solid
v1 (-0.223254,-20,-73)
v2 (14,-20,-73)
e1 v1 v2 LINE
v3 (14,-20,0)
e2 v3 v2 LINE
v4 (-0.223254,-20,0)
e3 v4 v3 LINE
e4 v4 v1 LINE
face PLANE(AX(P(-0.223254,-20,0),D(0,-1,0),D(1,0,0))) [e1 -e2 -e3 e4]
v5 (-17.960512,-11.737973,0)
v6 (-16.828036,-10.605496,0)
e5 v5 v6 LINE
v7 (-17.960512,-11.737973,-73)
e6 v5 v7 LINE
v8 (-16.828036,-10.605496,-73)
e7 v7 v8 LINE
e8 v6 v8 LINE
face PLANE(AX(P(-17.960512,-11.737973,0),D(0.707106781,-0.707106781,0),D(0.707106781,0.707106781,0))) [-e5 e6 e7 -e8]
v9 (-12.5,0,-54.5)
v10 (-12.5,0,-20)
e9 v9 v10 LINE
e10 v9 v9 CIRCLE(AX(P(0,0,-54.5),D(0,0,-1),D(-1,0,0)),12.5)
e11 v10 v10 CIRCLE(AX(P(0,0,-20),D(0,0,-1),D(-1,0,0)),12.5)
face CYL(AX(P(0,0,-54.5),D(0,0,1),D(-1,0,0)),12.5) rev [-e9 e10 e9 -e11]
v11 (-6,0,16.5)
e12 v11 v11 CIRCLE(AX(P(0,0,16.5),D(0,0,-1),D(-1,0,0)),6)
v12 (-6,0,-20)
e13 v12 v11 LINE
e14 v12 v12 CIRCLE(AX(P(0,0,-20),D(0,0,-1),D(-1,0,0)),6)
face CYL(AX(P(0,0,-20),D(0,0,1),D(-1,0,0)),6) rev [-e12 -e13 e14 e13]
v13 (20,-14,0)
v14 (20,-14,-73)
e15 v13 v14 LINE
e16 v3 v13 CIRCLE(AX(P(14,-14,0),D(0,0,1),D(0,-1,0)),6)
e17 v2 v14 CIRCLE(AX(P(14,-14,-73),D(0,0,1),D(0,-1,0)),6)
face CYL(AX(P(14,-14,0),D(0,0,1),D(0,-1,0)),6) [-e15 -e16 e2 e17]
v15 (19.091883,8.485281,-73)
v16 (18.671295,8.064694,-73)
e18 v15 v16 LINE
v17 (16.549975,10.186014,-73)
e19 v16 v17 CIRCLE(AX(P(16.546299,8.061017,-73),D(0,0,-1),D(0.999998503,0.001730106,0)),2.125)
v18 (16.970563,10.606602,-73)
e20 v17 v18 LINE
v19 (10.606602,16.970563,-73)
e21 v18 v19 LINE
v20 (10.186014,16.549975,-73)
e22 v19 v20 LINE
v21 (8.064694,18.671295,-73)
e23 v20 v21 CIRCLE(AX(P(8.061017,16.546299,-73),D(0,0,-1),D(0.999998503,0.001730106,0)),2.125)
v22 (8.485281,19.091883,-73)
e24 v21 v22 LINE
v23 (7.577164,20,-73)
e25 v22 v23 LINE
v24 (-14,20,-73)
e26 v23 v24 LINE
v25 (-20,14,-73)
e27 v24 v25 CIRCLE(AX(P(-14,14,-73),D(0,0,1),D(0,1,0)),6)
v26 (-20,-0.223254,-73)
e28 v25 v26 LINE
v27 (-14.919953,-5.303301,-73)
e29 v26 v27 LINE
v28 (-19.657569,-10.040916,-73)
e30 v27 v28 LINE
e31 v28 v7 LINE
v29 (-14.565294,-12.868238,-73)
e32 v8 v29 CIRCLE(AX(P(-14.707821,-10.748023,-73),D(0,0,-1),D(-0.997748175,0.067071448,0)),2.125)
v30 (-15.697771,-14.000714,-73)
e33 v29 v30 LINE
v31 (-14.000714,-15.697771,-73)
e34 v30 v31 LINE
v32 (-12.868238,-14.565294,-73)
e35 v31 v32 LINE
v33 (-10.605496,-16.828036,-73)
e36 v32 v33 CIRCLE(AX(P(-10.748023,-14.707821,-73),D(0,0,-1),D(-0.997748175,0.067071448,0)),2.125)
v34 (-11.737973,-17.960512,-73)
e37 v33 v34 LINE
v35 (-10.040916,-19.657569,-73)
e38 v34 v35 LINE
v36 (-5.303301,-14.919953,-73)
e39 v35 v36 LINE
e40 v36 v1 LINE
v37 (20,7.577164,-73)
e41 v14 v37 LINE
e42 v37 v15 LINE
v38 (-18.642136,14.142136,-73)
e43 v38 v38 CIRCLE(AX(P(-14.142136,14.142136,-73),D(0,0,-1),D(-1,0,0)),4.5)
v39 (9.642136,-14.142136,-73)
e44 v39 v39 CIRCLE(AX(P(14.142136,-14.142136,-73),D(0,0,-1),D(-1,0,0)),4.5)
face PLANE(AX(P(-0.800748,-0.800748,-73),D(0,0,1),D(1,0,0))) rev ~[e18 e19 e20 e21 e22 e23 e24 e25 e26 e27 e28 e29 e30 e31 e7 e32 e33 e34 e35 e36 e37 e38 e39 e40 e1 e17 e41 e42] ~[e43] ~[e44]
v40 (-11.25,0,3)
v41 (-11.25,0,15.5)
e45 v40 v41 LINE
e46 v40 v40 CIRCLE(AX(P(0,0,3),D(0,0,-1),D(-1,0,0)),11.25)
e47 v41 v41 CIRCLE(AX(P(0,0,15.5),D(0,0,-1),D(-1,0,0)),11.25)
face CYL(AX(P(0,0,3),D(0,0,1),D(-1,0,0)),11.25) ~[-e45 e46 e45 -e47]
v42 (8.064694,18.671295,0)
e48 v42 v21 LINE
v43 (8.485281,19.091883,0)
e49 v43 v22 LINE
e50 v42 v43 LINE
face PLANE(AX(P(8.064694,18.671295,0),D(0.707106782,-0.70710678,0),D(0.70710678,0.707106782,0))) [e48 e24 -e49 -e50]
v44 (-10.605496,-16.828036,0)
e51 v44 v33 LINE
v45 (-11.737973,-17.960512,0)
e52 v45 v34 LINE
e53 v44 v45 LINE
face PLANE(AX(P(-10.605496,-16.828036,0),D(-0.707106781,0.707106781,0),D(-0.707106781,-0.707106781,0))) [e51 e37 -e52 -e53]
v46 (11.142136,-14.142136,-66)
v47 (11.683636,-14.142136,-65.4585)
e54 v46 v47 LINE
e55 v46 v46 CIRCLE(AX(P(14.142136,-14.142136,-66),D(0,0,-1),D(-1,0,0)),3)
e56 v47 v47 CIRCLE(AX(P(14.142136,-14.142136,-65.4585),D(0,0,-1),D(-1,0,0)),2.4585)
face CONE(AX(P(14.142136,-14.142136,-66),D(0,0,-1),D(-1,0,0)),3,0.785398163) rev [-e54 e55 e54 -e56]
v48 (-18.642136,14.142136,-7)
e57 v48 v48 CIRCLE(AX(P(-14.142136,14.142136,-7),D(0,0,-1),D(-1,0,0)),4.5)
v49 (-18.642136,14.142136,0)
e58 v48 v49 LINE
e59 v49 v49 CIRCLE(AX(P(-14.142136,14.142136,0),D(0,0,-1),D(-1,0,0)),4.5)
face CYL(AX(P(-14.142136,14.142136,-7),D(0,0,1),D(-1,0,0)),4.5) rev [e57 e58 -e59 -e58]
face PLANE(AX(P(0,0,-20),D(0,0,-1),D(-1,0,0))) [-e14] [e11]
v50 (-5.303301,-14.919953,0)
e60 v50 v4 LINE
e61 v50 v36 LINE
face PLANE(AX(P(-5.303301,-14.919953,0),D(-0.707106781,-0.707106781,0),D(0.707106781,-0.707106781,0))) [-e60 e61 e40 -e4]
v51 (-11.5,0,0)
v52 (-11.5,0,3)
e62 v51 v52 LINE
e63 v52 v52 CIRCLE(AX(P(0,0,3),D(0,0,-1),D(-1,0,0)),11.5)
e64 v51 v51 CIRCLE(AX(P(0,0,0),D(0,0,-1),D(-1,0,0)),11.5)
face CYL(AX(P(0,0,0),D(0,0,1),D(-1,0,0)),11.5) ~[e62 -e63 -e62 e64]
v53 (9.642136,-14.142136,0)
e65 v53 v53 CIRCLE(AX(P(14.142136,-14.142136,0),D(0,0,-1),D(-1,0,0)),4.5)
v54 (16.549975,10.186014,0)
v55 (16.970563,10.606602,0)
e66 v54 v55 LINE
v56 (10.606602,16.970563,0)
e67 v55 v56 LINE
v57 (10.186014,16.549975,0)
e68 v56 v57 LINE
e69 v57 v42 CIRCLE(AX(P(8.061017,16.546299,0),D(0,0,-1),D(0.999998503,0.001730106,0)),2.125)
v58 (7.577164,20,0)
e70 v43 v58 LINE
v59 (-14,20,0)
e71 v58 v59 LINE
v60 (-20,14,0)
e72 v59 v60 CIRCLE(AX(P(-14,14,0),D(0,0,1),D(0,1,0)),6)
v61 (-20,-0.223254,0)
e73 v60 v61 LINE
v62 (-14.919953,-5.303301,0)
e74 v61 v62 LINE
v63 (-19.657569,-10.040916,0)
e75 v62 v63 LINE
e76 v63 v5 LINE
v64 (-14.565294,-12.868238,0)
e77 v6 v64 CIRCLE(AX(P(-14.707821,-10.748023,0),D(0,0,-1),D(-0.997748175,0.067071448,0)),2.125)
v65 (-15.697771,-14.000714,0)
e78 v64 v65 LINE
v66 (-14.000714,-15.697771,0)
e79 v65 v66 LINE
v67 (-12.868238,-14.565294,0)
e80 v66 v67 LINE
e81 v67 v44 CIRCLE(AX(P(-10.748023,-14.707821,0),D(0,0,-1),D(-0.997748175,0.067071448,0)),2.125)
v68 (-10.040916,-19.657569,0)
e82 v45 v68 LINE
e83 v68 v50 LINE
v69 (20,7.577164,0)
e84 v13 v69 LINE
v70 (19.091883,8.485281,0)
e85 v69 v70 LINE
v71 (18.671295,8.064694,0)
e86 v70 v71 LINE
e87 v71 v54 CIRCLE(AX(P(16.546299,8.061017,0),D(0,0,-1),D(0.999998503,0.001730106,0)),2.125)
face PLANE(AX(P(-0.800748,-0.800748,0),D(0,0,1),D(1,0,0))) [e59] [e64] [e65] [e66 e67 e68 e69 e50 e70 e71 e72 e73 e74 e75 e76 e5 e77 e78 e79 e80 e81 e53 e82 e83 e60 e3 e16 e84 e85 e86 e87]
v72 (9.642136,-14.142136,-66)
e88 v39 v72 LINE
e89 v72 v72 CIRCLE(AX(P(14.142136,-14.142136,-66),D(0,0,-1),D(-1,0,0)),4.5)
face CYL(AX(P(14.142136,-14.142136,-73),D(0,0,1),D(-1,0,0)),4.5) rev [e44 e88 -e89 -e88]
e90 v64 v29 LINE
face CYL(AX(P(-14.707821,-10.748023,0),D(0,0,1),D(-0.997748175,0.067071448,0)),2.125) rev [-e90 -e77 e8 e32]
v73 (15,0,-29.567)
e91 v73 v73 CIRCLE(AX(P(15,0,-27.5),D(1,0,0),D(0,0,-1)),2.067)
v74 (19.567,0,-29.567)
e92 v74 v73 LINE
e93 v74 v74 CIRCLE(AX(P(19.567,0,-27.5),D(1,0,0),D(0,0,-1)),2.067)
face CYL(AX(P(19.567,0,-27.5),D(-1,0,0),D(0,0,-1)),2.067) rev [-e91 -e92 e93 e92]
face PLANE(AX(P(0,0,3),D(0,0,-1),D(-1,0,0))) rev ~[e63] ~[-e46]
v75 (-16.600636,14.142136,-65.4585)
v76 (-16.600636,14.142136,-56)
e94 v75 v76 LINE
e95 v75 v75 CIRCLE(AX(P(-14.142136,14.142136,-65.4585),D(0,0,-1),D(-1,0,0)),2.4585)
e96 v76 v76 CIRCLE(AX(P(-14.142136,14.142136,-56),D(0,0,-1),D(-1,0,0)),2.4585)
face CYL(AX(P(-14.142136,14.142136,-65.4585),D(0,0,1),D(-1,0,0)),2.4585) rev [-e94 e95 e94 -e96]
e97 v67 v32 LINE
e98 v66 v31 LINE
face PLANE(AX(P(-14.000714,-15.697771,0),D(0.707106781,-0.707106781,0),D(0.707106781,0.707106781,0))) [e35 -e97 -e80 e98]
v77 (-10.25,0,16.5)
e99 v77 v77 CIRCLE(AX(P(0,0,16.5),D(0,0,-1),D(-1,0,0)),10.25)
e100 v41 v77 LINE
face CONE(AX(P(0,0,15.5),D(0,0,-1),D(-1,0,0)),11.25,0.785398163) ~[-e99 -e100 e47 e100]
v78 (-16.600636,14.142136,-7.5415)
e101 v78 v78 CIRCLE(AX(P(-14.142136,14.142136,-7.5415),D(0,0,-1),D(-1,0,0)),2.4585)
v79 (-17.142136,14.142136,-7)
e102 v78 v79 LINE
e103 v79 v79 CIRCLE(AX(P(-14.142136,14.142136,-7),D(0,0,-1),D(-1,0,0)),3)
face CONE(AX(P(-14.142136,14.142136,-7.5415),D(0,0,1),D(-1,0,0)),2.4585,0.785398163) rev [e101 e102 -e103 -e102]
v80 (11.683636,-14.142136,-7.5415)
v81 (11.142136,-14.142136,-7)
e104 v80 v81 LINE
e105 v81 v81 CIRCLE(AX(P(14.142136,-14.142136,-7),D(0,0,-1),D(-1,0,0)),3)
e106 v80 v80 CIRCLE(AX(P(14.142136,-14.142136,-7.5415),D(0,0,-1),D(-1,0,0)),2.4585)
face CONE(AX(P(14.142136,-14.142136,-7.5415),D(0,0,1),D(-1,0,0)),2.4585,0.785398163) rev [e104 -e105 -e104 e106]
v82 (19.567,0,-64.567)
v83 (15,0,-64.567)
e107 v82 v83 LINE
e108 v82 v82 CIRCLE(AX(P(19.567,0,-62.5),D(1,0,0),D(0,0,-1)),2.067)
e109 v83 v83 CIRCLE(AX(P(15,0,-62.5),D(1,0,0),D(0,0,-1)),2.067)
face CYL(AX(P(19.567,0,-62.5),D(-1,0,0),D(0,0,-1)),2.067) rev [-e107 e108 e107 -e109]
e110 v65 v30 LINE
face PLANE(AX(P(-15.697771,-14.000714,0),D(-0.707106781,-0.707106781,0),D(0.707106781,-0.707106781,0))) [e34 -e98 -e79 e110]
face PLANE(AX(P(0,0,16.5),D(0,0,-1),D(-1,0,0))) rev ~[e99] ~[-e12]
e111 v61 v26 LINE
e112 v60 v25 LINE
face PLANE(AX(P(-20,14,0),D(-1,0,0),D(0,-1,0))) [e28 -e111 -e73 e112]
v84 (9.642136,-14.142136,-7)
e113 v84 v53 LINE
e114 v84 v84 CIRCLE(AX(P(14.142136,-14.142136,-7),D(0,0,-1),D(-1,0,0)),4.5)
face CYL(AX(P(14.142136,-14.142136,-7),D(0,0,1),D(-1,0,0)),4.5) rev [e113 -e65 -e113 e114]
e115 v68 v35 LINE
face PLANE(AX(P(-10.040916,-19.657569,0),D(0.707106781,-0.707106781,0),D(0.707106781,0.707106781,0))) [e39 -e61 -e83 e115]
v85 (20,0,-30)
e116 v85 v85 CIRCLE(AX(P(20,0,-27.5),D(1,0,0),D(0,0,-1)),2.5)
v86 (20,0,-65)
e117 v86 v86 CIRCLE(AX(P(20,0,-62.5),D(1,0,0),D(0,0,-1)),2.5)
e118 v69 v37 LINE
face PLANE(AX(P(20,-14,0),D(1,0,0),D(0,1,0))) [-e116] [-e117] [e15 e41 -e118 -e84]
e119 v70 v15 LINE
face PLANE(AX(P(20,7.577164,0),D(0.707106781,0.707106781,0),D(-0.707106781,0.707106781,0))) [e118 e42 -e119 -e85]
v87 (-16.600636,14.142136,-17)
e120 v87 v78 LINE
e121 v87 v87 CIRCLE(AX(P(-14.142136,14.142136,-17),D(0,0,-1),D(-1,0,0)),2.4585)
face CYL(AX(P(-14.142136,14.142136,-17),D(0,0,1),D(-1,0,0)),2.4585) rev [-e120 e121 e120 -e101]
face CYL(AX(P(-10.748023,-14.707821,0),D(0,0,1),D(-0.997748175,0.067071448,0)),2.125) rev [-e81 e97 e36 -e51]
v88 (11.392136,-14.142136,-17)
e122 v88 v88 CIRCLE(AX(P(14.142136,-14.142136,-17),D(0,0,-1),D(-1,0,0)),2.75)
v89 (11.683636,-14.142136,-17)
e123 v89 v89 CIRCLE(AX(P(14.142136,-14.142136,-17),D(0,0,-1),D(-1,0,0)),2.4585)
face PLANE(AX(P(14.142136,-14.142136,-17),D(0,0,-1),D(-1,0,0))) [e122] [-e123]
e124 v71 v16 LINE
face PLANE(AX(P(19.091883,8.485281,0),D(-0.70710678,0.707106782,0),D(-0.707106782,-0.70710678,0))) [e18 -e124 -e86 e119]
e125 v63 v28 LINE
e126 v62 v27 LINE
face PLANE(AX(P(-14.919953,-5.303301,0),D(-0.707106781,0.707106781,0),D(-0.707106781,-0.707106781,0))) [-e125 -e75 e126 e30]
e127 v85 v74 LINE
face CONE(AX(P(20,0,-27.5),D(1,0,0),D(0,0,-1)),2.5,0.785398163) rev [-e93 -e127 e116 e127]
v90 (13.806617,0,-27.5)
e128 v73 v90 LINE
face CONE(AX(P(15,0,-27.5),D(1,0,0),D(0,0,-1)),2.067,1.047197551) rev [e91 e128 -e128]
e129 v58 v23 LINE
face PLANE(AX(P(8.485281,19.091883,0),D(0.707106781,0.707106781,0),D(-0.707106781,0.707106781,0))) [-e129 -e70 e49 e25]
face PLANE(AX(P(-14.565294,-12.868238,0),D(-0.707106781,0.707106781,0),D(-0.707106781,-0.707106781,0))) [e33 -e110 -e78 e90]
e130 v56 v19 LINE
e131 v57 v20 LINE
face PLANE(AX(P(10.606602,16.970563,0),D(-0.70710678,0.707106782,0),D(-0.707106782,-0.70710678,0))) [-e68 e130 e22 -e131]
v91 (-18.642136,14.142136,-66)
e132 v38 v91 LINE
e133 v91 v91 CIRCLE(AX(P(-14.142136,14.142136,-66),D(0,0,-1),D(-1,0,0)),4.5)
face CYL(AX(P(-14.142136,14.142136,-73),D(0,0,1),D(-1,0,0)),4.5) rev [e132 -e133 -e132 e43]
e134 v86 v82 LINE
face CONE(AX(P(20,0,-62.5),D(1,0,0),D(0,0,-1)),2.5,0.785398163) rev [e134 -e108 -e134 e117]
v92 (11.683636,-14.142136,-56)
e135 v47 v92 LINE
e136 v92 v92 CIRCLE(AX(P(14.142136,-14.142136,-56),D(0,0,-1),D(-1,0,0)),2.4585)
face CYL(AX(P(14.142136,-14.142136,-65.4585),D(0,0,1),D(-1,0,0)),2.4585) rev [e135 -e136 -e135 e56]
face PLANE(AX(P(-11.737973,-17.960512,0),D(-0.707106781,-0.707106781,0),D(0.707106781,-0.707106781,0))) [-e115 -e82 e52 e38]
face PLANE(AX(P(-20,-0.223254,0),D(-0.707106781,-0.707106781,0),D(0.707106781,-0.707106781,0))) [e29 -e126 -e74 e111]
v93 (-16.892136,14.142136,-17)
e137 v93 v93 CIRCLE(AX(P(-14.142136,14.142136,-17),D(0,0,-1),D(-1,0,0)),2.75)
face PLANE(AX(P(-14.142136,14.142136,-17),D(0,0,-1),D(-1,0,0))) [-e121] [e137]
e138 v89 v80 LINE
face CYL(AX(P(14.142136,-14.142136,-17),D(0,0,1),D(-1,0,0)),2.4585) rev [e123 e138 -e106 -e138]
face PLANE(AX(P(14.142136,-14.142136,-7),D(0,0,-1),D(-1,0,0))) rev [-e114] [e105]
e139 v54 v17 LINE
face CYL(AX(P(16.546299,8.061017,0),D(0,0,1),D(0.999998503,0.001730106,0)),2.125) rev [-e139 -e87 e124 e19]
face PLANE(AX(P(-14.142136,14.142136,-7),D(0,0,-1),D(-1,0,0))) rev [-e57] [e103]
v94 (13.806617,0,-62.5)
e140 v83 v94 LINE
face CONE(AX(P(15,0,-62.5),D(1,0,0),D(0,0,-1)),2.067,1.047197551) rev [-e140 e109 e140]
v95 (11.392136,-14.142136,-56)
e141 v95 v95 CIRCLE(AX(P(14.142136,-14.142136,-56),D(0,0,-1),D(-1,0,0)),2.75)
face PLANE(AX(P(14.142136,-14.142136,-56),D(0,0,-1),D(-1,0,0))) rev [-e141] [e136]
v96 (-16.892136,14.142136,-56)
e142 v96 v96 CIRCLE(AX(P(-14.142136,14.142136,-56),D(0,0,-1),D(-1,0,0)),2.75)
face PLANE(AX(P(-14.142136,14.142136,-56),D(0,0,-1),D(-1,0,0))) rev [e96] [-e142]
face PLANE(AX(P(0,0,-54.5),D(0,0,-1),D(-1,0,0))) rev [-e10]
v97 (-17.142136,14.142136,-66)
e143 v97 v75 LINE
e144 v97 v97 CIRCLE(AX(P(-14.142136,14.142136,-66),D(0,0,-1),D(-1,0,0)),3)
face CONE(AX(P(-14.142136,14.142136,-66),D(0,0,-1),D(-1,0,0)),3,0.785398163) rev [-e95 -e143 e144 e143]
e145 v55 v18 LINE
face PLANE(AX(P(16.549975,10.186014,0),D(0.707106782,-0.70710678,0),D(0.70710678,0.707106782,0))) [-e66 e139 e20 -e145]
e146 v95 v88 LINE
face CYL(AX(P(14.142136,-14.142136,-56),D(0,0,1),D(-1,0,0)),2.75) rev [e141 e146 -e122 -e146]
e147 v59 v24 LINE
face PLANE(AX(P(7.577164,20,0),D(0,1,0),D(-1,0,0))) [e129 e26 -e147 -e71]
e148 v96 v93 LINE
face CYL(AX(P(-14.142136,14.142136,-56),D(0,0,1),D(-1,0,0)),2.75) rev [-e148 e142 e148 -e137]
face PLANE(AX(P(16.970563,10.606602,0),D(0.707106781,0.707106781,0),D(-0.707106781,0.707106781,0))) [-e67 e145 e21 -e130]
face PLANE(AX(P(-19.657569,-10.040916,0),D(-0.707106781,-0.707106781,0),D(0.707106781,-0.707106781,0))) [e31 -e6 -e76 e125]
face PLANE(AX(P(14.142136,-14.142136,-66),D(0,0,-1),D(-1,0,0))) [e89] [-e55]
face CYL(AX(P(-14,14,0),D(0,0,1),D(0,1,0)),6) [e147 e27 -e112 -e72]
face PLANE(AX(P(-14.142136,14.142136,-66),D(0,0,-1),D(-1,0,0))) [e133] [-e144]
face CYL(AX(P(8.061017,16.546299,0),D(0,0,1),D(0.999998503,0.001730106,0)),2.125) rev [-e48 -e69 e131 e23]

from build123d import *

# Parameters (mm, degrees)
EXTRUDE_1_DEPTH = 73


with BuildPart() as part:
    # 草图1 → 凸台-拉伸1 (new body)
    with BuildSketch(Plane.XY):
        with BuildLine():
            Line((-20, 14), (-20, -0.223253942))
            Line((-20, -0.223253942), (-14.919953083, -5.303300859))
            Line((-14.919953083, -5.303300859), (-19.657568517, -10.040916293))
            Line((-19.657568517, -10.040916293), (-17.960512242, -11.737972568))
            Line((-17.960512242, -11.737972568), (-16.828035921, -10.605496246))
            ThreePointArc((-16.828035921, -10.605496246), (-13.205219139, -9.245421164), (-14.565294221, -12.868237946))
            Line((-14.565294221, -12.868237946), (-15.697770542, -14.000714267))
            Line((-15.697770542, -14.000714267), (-14.000714267, -15.697770542))
            Line((-14.000714267, -15.697770542), (-12.868237946, -14.565294221))
            ThreePointArc((-12.868237946, -14.565294221), (-9.245421164, -13.205219139), (-10.605496246, -16.828035921))
            Line((-10.605496246, -16.828035921), (-11.737972568, -17.960512242))
            Line((-11.737972568, -17.960512242), (-10.040916293, -19.657568517))
            Line((-10.040916293, -19.657568517), (-5.303300859, -14.919953083))
            Line((-5.303300859, -14.919953083), (-0.223253942, -20))
            Line((-0.223253942, -20), (14, -20))
            ThreePointArc((14, -20), (18.242640687, -18.242640687), (20, -14))
            Line((20, -14), (20, 7.577164466))
            Line((20, 7.577164466), (19.091883092, 8.485281374))
            Line((19.091883092, 8.485281374), (18.671295499, 8.064693782))
            ThreePointArc((18.671295499, 8.064693782), (15.04369677, 6.558415396), (16.549975156, 10.186014125))
            Line((16.549975156, 10.186014125), (16.970562748, 10.606601718))
            Line((16.970562748, 10.606601718), (10.606601718, 16.970562748))
            Line((10.606601718, 16.970562748), (10.186014125, 16.549975156))
            ThreePointArc((10.186014125, 16.549975156), (6.558415396, 15.04369677), (8.064693782, 18.671295499))
            Line((8.064693782, 18.671295499), (8.485281374, 19.091883092))
            Line((8.485281374, 19.091883092), (7.577164466, 20))
            Line((7.577164466, 20), (-14, 20))
            ThreePointArc((-14, 20), (-18.242640687, 18.242640687), (-20, 14))
        make_face()
    extrude(amount=-EXTRUDE_1_DEPTH)

    # 草图2 → 切除-旋转1 (revolve, cut)
    with BuildSketch(Plane(origin=(0, 0, 0), x_dir=(0.7071067811865476, -0.7071067811865475, 0), z_dir=(0.7071067811865475, 0.7071067811865476, 0)), mode=Mode.PRIVATE) as cut_revolve_1_sk:
        Polygon((20, 73), (24.5, 73), (24.5, 66), (23, 66), (22.4585, 65.4585), (22.4585, 56), (22.75, 56), (22.75, 17), (22.4585, 17), (22.4585, 7.5415), (23, 7), (24.5, 7), (24.5, 0), (20, 0), align=None)
    revolve(cut_revolve_1_sk.sketch.rotate(Axis((14.142135624, -14.142135624, 0), (0, 0, -1)), 135), axis=Axis((14.142135624, -14.142135624, 0), (0, 0, -1)), mode=Mode.SUBTRACT)

    # 草图3 → 切除-旋转2 (revolve, cut)
    with BuildSketch(Plane(origin=(0, 0, 0), x_dir=(0.7071067811865476, -0.7071067811865475, 0), z_dir=(0.7071067811865475, 0.7071067811865476, 0)), mode=Mode.PRIVATE) as cut_revolve_2_sk:
        Polygon((-20, 73), (-15.5, 73), (-15.5, 66), (-17, 66), (-17.5415, 65.4585), (-17.5415, 56), (-17.25, 56), (-17.25, 17), (-17.5415, 17), (-17.5415, 7.5415), (-17, 7), (-15.5, 7), (-15.5, 0), (-20, 0), align=None)
    revolve(cut_revolve_2_sk.sketch.rotate(Axis((-14.142135624, 14.142135624, 0), (0, 0, -1)), 135), axis=Axis((-14.142135624, 14.142135624, 0), (0, 0, -1)), mode=Mode.SUBTRACT)

    # 草图4 → 旋转1 (revolve)
    with BuildSketch(Plane(origin=(0, 0, 0), x_dir=(1, 0, 0), z_dir=(0, 1, 0)), mode=Mode.PRIVATE) as revolve_1_sk:
        Polygon((0, 0), (11.5, 0), (11.5, -3), (11.25, -3), (11.25, -15.5), (10.25, -16.5), (0, -16.5), align=None)
    revolve(revolve_1_sk.sketch.rotate(Axis((0, 0, 16.5), (0, 0, -1)), 180), axis=Axis((0, 0, 16.5), (0, 0, -1)))

    # 草图5 → 切除-旋转3 (revolve, cut)
    with BuildSketch(Plane(origin=(0, 0, 0), x_dir=(1, 0, 0), z_dir=(0, 1, 0)), mode=Mode.PRIVATE) as cut_revolve_3_sk:
        Polygon((0, 54.5), (12.5, 54.5), (12.5, 20), (6, 20), (6, -16.5), (0, -16.5), align=None)
    revolve(cut_revolve_3_sk.sketch.rotate(Axis((0, 0, 16.5), (0, 0, -1)), 180), axis=Axis((0, 0, 16.5), (0, 0, -1)), mode=Mode.SUBTRACT)

    # 草图6 → 切除-旋转4 (revolve, cut)
    with BuildSketch(Plane(origin=(0, 0, 0), x_dir=(1, 0, 0), z_dir=(0, 1, 0)), mode=Mode.PRIVATE) as cut_revolve_4_sk:
        Polygon((20, 27.5), (20, 25), (19.567, 25.433), (15, 25.433), (13.806616994, 27.5), align=None)
    revolve(cut_revolve_4_sk.sketch.rotate(Axis((13.806616994, 0, -27.5), (1, 0, 0)), 180), axis=Axis((13.806616994, 0, -27.5), (1, 0, 0)), mode=Mode.SUBTRACT)

    # 草图7 → 切除-旋转5 (revolve, cut)
    with BuildSketch(Plane(origin=(0, 0, 0), x_dir=(1, 0, 0), z_dir=(0, 1, 0)), mode=Mode.PRIVATE) as cut_revolve_5_sk:
        Polygon((20, 62.5), (20, 60), (19.567, 60.433), (15, 60.433), (13.806616994, 62.5), align=None)
    revolve(cut_revolve_5_sk.sketch.rotate(Axis((13.806616994, 0, -62.5), (1, 0, 0)), 180), axis=Axis((13.806616994, 0, -62.5), (1, 0, 0)), mode=Mode.SUBTRACT)


solid = part.part
